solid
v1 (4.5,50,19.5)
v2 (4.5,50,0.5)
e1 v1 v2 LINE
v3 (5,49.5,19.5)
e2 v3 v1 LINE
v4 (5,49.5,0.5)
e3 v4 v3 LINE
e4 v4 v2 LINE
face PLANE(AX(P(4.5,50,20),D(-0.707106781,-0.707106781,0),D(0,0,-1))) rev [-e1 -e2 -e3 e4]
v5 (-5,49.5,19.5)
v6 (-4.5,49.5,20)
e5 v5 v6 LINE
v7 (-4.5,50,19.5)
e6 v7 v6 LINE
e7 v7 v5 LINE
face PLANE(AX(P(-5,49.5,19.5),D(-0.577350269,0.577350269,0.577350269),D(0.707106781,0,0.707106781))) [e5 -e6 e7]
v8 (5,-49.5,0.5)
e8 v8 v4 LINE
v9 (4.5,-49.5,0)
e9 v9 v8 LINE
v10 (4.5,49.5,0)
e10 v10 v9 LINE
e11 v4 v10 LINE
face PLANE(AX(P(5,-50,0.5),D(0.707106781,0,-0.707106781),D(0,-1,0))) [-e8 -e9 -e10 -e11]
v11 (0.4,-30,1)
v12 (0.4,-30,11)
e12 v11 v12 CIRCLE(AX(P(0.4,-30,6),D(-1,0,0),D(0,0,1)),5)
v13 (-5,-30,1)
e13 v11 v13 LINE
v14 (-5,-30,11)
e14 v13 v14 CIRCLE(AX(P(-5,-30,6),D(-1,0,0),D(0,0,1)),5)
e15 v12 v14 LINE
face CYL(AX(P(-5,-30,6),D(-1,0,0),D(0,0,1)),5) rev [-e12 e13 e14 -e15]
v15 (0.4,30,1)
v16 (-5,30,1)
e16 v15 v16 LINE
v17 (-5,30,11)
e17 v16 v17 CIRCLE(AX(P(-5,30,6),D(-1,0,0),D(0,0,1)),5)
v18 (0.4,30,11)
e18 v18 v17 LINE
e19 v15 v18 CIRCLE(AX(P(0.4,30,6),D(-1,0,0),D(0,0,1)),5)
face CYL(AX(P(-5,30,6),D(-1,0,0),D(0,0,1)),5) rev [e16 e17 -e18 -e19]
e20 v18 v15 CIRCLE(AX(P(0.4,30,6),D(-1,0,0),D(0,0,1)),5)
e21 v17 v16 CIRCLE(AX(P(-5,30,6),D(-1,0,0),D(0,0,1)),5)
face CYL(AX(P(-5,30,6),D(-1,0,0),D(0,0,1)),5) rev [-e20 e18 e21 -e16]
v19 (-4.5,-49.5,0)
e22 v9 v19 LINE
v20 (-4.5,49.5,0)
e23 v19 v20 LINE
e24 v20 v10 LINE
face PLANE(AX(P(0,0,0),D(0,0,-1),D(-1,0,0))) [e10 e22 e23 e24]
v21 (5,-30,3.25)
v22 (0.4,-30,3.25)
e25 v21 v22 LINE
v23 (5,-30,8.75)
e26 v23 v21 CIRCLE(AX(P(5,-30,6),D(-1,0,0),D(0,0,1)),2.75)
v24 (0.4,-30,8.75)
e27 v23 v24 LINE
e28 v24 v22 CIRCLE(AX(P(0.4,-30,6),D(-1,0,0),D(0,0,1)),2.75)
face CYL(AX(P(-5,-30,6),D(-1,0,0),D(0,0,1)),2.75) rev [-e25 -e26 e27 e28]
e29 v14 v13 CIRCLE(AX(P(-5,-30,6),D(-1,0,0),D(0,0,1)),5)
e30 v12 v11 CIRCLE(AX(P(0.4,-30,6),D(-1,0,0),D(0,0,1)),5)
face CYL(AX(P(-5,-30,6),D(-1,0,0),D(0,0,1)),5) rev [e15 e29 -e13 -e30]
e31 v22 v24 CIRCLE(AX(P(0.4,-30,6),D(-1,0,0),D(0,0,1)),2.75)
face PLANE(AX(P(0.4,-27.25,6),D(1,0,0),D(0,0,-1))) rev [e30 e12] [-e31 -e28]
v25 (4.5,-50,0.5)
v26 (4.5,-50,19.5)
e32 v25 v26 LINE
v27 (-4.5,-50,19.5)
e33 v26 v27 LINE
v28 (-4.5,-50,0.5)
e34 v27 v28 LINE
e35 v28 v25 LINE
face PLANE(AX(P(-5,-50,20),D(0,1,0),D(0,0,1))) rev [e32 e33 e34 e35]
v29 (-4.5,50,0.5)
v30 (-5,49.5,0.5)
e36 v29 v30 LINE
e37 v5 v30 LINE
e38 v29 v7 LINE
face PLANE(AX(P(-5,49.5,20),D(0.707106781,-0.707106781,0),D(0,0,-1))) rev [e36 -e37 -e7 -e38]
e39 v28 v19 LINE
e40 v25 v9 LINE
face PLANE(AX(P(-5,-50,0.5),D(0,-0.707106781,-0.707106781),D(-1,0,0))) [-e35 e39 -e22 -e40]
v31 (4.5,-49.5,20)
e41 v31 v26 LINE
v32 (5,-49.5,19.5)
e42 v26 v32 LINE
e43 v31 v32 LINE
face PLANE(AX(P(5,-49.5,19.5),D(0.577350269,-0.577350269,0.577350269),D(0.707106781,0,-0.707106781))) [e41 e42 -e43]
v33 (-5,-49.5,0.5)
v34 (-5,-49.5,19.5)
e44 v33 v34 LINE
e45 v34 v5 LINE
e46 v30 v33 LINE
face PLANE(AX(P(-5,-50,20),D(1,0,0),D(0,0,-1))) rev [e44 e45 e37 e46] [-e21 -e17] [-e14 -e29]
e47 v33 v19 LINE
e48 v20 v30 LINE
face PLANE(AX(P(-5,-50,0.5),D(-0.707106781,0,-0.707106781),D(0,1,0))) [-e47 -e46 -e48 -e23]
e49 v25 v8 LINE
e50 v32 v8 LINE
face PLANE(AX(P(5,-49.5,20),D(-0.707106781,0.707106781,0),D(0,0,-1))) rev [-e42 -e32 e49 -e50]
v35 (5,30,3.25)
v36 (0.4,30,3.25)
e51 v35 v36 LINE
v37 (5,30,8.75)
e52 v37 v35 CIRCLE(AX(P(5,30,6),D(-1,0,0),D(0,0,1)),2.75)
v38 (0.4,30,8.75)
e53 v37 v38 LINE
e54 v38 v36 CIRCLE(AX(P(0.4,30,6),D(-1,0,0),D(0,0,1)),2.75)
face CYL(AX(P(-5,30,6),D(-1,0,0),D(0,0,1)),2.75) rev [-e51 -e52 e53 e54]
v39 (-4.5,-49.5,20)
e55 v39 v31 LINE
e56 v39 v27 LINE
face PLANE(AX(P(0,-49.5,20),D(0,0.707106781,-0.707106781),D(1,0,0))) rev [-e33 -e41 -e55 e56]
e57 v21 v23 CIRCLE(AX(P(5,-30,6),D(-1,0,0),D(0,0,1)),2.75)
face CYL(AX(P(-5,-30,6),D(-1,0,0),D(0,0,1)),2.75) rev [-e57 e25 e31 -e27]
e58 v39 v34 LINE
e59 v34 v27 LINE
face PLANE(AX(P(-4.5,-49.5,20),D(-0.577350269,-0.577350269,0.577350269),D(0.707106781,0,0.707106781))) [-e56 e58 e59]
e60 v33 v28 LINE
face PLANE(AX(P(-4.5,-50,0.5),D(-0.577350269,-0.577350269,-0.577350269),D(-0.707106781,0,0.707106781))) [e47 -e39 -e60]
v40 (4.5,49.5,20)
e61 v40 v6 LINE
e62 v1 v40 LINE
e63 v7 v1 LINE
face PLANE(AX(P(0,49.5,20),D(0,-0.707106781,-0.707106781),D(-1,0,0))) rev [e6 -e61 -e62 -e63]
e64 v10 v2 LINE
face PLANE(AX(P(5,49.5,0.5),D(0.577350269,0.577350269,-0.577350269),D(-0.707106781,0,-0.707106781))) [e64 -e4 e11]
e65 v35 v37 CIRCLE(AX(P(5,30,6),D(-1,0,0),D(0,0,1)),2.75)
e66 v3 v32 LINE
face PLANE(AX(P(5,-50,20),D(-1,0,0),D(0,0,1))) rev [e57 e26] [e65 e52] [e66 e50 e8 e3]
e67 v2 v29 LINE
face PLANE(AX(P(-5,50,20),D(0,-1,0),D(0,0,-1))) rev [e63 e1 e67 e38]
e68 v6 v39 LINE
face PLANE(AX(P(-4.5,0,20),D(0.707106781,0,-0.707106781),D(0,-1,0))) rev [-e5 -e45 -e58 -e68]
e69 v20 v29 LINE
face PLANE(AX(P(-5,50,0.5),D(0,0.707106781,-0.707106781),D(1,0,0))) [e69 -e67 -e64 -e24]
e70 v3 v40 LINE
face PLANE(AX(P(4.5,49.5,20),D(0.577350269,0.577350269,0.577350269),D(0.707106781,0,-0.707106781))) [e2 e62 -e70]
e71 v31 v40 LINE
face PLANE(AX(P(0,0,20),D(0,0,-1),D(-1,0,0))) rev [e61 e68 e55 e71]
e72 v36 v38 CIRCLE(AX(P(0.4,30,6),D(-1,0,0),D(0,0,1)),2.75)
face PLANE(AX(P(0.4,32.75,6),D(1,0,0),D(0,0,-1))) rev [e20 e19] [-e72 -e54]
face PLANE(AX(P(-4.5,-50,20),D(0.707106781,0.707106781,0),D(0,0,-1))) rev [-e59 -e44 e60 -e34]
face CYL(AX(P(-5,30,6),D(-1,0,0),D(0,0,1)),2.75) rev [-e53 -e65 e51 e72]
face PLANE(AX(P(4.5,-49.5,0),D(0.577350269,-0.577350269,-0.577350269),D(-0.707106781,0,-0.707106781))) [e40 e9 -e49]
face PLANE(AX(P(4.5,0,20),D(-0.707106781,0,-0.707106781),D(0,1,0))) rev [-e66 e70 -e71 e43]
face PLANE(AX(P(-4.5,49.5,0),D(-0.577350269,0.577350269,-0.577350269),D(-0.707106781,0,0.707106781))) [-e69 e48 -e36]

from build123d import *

# Parameters (mm, degrees)
SKETCH_1_W                   = 10
SKETCH_1_H                   = 100
EXTRUDE_1_DEPTH              = 20
HOLE_WIZARD_M5_1_D           = 5.5
HOLE_WIZARD_M5_1_CBORE_D     = 10
HOLE_WIZARD_M5_1_CBORE_DEPTH = 5.4
CHAMFER_1_SIZE               = 0.5


with BuildPart() as part:
    # 草图1 → 凸台-拉伸1 (new body)
    with BuildSketch(Plane.XY):
        Rectangle(SKETCH_1_W, SKETCH_1_H)
    extrude(amount=EXTRUDE_1_DEPTH)

    # M5 六角凹头螺钉的柱形沉头孔1 (through all)
    with Locations(Plane.ZY.offset(5)):
        with Locations((6, 30), (6, -30)):
            CounterBoreHole(HOLE_WIZARD_M5_1_D / 2, HOLE_WIZARD_M5_1_CBORE_D / 2, HOLE_WIZARD_M5_1_CBORE_DEPTH)

    # 倒角1
    chamfer_1_edges = [part.edges().sort_by_distance(p)[0] for p in [
        (-5, 0, 20),
        (0, -50, 20),
        (5, 0, 20),
        (0, -50, 0),
        (-5, 0, 0),
        (0, 50, 0),
        (5, 0, 0),
        (5, -50, 10),
        (-5, -50, 10),
        (-5, 50, 10),
        (5, 50, 10),
        (0, 50, 20),
    ]]
    chamfer(chamfer_1_edges, length=CHAMFER_1_SIZE)


solid = part.part
